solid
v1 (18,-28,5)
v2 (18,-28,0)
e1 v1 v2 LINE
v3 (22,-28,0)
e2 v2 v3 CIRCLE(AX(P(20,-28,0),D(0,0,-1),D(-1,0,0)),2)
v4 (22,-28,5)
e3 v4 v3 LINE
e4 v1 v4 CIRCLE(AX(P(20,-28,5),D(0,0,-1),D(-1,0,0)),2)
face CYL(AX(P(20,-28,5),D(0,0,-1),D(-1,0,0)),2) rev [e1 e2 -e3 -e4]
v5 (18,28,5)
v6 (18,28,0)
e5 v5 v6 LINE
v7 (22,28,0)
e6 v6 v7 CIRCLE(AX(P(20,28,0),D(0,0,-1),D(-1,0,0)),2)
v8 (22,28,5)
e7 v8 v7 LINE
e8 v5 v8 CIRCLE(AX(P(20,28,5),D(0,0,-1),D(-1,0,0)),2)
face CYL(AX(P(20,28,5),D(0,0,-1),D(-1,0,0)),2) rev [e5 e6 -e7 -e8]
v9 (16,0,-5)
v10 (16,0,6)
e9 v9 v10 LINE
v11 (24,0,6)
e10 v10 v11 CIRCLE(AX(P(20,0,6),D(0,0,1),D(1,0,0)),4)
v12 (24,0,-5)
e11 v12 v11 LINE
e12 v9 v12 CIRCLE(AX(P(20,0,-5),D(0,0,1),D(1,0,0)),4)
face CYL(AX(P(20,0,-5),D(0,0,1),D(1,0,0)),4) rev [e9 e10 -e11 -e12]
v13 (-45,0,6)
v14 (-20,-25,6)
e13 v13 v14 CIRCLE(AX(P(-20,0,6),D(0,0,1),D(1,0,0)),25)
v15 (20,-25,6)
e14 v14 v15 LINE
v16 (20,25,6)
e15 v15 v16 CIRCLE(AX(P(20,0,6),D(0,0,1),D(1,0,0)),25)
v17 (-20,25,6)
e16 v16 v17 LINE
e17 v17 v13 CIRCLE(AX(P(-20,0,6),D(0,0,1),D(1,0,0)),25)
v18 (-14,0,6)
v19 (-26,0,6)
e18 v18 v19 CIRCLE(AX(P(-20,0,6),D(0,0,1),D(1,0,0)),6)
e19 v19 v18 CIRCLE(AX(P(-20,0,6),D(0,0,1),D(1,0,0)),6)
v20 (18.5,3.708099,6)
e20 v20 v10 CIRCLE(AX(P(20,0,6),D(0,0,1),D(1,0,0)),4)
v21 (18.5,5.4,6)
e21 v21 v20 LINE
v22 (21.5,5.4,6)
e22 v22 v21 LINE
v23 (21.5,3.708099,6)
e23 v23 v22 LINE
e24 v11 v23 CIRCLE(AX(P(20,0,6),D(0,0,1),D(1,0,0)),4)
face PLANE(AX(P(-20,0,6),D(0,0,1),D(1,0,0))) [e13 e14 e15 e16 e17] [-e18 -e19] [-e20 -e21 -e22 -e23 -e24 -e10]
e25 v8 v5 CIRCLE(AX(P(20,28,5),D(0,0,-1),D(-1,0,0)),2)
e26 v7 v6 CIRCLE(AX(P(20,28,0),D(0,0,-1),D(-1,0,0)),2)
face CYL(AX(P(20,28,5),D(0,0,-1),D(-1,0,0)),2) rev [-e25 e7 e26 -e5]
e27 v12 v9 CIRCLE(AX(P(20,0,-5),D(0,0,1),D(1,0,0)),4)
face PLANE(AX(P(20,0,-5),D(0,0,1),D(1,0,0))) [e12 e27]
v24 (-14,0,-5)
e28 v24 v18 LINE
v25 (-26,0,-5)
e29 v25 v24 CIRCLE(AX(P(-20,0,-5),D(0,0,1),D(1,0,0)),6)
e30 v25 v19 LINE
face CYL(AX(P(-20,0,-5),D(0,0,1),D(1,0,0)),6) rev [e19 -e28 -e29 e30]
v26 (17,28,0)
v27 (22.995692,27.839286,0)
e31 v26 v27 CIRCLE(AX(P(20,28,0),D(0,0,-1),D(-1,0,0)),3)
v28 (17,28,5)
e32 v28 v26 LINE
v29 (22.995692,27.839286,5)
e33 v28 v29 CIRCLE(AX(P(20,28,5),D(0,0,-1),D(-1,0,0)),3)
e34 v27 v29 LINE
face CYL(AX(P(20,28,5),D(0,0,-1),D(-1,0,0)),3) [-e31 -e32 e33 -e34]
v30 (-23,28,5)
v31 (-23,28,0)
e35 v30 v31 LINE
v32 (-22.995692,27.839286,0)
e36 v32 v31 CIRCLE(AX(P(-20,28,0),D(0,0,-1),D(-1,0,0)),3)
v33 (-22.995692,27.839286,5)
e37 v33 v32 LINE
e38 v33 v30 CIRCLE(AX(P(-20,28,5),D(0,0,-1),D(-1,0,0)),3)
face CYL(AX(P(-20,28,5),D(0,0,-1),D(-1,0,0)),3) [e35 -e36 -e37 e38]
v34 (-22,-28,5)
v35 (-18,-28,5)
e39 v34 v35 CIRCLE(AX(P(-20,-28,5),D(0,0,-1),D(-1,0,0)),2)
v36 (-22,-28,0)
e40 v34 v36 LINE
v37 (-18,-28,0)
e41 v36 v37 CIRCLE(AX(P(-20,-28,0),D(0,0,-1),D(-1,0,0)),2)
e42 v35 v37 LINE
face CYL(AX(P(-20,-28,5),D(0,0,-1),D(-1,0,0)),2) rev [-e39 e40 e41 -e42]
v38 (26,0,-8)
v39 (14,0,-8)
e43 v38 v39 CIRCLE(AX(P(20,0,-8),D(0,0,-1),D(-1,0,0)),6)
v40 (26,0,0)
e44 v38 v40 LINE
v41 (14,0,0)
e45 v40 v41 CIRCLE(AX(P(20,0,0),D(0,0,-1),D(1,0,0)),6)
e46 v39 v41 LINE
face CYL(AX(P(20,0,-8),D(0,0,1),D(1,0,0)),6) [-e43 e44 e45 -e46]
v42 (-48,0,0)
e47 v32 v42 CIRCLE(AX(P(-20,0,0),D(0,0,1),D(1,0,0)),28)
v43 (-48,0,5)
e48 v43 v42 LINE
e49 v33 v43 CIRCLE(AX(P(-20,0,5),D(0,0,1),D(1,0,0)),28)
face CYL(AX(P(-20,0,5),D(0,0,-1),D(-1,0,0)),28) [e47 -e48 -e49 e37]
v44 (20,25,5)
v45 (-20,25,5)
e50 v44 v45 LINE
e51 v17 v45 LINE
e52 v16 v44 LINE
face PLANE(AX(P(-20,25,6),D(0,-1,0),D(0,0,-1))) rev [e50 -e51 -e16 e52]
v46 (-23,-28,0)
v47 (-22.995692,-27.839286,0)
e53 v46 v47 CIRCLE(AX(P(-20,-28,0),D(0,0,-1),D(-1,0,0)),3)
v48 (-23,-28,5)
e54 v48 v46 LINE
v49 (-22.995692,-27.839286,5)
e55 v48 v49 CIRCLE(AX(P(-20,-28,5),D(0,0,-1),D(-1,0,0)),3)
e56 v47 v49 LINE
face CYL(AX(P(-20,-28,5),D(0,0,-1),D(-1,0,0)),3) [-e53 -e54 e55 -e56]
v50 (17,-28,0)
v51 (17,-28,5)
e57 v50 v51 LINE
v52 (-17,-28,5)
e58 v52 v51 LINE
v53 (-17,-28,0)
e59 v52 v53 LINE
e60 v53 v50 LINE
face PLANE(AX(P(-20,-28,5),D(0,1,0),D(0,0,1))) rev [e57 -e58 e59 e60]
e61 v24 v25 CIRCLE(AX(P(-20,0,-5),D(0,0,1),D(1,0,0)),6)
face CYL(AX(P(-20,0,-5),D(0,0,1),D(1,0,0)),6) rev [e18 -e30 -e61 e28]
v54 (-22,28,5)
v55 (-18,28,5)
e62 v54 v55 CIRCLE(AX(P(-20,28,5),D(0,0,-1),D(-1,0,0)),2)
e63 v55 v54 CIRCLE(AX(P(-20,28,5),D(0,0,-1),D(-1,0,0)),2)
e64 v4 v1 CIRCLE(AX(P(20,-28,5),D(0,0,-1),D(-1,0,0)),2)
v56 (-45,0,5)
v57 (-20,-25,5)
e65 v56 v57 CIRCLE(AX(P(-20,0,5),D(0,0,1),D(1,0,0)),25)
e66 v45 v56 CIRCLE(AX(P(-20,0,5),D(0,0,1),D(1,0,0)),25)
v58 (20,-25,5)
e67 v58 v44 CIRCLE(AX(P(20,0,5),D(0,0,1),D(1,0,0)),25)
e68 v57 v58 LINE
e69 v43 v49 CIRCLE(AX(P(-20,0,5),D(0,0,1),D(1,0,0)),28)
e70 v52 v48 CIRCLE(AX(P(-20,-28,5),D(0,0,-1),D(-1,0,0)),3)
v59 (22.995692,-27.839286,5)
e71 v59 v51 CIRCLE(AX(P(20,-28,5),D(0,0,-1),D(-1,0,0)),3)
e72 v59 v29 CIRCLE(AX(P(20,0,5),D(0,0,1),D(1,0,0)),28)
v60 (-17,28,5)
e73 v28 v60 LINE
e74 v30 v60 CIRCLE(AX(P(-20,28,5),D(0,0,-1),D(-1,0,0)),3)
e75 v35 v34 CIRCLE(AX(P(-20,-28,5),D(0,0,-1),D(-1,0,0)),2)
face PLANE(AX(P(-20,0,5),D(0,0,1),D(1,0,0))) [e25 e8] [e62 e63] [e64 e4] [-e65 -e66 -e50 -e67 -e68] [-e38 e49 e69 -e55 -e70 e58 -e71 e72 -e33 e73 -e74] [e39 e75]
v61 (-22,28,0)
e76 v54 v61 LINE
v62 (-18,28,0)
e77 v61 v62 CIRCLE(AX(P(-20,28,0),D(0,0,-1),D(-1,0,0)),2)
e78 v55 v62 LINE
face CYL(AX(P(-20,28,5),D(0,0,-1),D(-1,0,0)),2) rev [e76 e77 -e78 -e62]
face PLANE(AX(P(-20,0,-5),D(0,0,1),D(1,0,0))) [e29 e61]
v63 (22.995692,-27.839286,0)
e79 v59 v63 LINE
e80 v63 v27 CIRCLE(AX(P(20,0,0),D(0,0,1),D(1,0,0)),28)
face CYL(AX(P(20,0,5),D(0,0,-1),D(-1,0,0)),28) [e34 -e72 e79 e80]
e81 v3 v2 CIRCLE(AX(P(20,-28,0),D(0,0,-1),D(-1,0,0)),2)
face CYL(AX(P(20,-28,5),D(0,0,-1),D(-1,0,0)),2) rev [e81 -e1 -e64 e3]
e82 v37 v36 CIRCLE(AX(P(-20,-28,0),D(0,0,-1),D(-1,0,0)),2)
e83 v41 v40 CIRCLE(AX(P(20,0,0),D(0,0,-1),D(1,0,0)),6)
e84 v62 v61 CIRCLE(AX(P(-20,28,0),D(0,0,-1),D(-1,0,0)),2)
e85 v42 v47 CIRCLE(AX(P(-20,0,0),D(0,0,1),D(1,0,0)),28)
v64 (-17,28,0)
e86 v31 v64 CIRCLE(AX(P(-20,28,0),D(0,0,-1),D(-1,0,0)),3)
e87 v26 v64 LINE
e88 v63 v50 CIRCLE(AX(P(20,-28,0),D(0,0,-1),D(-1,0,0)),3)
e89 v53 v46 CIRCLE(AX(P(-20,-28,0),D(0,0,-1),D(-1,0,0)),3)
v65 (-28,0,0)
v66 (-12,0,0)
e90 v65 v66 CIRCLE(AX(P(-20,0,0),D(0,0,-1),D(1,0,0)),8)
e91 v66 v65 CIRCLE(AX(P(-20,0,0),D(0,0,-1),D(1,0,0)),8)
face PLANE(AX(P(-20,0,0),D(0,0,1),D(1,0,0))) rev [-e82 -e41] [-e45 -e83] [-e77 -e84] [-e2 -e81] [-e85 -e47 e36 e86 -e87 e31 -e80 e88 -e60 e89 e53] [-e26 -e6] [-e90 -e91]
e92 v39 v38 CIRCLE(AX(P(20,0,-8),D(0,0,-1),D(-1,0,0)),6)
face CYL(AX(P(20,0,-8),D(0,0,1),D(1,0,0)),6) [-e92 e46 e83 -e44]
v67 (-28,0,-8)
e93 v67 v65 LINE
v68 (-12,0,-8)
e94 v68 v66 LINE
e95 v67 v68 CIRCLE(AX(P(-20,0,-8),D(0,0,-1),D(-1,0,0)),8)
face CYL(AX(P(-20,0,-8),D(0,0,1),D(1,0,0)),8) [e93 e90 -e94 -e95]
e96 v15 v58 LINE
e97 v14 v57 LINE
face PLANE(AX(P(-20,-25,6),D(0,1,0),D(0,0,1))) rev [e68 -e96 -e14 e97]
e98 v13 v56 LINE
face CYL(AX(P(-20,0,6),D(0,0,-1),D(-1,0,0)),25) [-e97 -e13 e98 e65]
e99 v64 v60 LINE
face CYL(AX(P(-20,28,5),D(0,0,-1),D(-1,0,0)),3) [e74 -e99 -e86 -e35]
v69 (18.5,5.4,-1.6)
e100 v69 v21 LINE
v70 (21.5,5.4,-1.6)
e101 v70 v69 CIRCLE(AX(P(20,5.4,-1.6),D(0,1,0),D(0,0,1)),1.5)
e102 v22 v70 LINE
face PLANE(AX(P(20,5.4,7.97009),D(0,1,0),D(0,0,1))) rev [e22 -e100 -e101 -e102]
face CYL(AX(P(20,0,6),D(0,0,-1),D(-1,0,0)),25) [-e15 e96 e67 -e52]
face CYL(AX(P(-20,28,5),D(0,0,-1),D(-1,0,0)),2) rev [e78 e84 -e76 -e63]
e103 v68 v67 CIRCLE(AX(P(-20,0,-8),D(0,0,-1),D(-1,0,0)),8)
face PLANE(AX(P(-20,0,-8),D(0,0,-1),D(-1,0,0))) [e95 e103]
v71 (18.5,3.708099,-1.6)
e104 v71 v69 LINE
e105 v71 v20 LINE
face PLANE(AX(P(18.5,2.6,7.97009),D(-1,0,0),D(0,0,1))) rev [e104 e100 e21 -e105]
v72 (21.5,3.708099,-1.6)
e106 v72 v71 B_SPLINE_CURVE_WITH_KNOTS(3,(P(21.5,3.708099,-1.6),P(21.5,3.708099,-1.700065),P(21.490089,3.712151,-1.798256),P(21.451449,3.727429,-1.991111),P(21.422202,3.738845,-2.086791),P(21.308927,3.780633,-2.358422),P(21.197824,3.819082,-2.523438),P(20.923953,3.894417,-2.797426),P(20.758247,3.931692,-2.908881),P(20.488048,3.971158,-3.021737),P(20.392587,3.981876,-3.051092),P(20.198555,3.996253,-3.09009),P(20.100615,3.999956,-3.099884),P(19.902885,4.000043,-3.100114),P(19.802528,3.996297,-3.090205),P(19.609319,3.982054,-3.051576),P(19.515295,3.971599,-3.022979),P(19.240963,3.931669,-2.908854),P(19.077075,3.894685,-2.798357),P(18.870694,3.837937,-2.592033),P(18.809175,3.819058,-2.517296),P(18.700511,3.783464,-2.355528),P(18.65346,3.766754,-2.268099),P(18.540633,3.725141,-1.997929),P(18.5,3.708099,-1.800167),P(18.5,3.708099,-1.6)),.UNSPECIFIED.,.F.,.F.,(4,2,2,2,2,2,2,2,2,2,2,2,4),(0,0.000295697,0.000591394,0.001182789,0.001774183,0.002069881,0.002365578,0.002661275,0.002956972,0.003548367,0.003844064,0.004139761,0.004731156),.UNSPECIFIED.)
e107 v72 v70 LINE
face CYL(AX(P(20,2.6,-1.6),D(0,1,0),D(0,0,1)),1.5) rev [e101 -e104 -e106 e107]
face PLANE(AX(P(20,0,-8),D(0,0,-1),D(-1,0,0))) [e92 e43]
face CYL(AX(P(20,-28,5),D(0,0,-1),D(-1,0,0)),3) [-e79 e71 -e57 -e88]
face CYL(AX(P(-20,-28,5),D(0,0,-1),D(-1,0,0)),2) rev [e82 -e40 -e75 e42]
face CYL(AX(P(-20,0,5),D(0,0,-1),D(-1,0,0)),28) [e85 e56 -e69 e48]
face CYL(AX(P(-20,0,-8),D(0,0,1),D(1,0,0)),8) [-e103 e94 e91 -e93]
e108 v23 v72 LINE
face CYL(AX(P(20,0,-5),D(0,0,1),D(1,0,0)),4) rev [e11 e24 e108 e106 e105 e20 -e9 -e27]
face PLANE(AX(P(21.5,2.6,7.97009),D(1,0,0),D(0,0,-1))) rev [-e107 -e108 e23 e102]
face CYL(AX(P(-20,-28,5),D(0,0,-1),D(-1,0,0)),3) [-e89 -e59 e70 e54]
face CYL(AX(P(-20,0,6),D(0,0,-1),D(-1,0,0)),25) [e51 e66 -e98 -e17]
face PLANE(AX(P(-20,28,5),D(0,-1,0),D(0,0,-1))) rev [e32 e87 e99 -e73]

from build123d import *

# Parameters (mm, degrees)
BOSS_EXTRUDE1_DEPTH = 5
BOSS_EXTRUDE2_DEPTH = 1
SKETCH5_R           = 3
BOSS_EXTRUDE3_DEPTH = 5
SKETCH6_R           = 2
CUT_EXTRUDE1_DEPTH  = 5
SKETCH7_R           = 6
SKETCH7_R_2         = 8
BOSS_EXTRUDE4_DEPTH = 8
SKETCH8_R           = 6
SKETCH8_R_2         = 4
CUT_EXTRUDE2_DEPTH  = 11
CUT_EXTRUDE3_DEPTH  = 1.4


with BuildPart() as part:
    # Sketch2 → Boss-Extrude1 (new body)
    with BuildSketch(Plane.XY):
        with BuildLine():
            Line((-20, 28), (20, 28))
            ThreePointArc((20, 28), (48, 0), (20, -28))
            Line((20, -28), (-20, -28))
            ThreePointArc((-20, -28), (-48, 0), (-20, 28))
        make_face()
    extrude(amount=BOSS_EXTRUDE1_DEPTH)

    # Sketch4 → Boss-Extrude2 (add)
    with BuildSketch(Plane.XY.offset(5)):
        with BuildLine():
            Line((-20, 25), (20, 25))
            ThreePointArc((20, 25), (45, 0), (20, -25))
            Line((20, -25), (-20, -25))
            ThreePointArc((-20, -25), (-45, 0), (-20, 25))
        make_face()
    extrude(amount=BOSS_EXTRUDE2_DEPTH)

    # Sketch5 → Boss-Extrude3 (add)
    with BuildSketch(Plane(origin=(0, 0, 0), x_dir=(-1, 0, 0), z_dir=(0, 0, -1))):
        with Locations((-20, 28)):
            Circle(SKETCH5_R)
        with Locations((20, 28)):
            Circle(SKETCH5_R)
        with Locations((-20, -28)):
            Circle(SKETCH5_R)
        with Locations((20, -28)):
            Circle(SKETCH5_R)
    extrude(amount=-BOSS_EXTRUDE3_DEPTH)

    # Sketch6 → Cut-Extrude1 (cut)
    with BuildSketch(Plane(origin=(0, 0, 0), x_dir=(-1, 0, 0), z_dir=(0, 0, -1))):
        with Locations((-20, 28)):
            Circle(SKETCH6_R)
        with Locations((20, 28)):
            Circle(SKETCH6_R)
        with Locations((-20, -28)):
            Circle(SKETCH6_R)
        with Locations((20, -28)):
            Circle(SKETCH6_R)
    extrude(amount=-CUT_EXTRUDE1_DEPTH, mode=Mode.SUBTRACT)

    # Sketch7 → Boss-Extrude4 (add)
    with BuildSketch(Plane(origin=(0, 0, 0), x_dir=(-1, 0, 0), z_dir=(0, 0, -1))):
        with Locations(Location((-20, 0, 0), (0, 0, 180))):
            Circle(SKETCH7_R)
        with Locations(Location((20, 0, 0), (0, 0, 180))):
            Circle(SKETCH7_R_2)
    extrude(amount=BOSS_EXTRUDE4_DEPTH)

    # Sketch8 → Cut-Extrude2 (cut)
    with BuildSketch(Plane.XY.offset(6)):
        with Locations((-20, 0)):
            Circle(SKETCH8_R)
        with Locations((20, 0)):
            Circle(SKETCH8_R_2)
    extrude(amount=-CUT_EXTRUDE2_DEPTH, mode=Mode.SUBTRACT)

    # Sketch9 → Cut-Extrude3 (cut, symmetric)
    with BuildSketch(Plane(origin=(0, 4, 0), x_dir=(1, 0, 0), z_dir=(0, 1, 0))):
        with BuildLine():
            Line((18.5, -7.970089987), (18.5, 1.6))
            ThreePointArc((18.5, 1.6), (20, 3.1), (21.5, 1.6))
            Line((21.5, 1.6), (21.5, -7.970089987))
            ThreePointArc((21.5, -7.970089987), (20, -9.470089987), (18.5, -7.970089987))
        make_face()
    extrude(amount=CUT_EXTRUDE3_DEPTH, both=True, mode=Mode.SUBTRACT)


solid = part.part
